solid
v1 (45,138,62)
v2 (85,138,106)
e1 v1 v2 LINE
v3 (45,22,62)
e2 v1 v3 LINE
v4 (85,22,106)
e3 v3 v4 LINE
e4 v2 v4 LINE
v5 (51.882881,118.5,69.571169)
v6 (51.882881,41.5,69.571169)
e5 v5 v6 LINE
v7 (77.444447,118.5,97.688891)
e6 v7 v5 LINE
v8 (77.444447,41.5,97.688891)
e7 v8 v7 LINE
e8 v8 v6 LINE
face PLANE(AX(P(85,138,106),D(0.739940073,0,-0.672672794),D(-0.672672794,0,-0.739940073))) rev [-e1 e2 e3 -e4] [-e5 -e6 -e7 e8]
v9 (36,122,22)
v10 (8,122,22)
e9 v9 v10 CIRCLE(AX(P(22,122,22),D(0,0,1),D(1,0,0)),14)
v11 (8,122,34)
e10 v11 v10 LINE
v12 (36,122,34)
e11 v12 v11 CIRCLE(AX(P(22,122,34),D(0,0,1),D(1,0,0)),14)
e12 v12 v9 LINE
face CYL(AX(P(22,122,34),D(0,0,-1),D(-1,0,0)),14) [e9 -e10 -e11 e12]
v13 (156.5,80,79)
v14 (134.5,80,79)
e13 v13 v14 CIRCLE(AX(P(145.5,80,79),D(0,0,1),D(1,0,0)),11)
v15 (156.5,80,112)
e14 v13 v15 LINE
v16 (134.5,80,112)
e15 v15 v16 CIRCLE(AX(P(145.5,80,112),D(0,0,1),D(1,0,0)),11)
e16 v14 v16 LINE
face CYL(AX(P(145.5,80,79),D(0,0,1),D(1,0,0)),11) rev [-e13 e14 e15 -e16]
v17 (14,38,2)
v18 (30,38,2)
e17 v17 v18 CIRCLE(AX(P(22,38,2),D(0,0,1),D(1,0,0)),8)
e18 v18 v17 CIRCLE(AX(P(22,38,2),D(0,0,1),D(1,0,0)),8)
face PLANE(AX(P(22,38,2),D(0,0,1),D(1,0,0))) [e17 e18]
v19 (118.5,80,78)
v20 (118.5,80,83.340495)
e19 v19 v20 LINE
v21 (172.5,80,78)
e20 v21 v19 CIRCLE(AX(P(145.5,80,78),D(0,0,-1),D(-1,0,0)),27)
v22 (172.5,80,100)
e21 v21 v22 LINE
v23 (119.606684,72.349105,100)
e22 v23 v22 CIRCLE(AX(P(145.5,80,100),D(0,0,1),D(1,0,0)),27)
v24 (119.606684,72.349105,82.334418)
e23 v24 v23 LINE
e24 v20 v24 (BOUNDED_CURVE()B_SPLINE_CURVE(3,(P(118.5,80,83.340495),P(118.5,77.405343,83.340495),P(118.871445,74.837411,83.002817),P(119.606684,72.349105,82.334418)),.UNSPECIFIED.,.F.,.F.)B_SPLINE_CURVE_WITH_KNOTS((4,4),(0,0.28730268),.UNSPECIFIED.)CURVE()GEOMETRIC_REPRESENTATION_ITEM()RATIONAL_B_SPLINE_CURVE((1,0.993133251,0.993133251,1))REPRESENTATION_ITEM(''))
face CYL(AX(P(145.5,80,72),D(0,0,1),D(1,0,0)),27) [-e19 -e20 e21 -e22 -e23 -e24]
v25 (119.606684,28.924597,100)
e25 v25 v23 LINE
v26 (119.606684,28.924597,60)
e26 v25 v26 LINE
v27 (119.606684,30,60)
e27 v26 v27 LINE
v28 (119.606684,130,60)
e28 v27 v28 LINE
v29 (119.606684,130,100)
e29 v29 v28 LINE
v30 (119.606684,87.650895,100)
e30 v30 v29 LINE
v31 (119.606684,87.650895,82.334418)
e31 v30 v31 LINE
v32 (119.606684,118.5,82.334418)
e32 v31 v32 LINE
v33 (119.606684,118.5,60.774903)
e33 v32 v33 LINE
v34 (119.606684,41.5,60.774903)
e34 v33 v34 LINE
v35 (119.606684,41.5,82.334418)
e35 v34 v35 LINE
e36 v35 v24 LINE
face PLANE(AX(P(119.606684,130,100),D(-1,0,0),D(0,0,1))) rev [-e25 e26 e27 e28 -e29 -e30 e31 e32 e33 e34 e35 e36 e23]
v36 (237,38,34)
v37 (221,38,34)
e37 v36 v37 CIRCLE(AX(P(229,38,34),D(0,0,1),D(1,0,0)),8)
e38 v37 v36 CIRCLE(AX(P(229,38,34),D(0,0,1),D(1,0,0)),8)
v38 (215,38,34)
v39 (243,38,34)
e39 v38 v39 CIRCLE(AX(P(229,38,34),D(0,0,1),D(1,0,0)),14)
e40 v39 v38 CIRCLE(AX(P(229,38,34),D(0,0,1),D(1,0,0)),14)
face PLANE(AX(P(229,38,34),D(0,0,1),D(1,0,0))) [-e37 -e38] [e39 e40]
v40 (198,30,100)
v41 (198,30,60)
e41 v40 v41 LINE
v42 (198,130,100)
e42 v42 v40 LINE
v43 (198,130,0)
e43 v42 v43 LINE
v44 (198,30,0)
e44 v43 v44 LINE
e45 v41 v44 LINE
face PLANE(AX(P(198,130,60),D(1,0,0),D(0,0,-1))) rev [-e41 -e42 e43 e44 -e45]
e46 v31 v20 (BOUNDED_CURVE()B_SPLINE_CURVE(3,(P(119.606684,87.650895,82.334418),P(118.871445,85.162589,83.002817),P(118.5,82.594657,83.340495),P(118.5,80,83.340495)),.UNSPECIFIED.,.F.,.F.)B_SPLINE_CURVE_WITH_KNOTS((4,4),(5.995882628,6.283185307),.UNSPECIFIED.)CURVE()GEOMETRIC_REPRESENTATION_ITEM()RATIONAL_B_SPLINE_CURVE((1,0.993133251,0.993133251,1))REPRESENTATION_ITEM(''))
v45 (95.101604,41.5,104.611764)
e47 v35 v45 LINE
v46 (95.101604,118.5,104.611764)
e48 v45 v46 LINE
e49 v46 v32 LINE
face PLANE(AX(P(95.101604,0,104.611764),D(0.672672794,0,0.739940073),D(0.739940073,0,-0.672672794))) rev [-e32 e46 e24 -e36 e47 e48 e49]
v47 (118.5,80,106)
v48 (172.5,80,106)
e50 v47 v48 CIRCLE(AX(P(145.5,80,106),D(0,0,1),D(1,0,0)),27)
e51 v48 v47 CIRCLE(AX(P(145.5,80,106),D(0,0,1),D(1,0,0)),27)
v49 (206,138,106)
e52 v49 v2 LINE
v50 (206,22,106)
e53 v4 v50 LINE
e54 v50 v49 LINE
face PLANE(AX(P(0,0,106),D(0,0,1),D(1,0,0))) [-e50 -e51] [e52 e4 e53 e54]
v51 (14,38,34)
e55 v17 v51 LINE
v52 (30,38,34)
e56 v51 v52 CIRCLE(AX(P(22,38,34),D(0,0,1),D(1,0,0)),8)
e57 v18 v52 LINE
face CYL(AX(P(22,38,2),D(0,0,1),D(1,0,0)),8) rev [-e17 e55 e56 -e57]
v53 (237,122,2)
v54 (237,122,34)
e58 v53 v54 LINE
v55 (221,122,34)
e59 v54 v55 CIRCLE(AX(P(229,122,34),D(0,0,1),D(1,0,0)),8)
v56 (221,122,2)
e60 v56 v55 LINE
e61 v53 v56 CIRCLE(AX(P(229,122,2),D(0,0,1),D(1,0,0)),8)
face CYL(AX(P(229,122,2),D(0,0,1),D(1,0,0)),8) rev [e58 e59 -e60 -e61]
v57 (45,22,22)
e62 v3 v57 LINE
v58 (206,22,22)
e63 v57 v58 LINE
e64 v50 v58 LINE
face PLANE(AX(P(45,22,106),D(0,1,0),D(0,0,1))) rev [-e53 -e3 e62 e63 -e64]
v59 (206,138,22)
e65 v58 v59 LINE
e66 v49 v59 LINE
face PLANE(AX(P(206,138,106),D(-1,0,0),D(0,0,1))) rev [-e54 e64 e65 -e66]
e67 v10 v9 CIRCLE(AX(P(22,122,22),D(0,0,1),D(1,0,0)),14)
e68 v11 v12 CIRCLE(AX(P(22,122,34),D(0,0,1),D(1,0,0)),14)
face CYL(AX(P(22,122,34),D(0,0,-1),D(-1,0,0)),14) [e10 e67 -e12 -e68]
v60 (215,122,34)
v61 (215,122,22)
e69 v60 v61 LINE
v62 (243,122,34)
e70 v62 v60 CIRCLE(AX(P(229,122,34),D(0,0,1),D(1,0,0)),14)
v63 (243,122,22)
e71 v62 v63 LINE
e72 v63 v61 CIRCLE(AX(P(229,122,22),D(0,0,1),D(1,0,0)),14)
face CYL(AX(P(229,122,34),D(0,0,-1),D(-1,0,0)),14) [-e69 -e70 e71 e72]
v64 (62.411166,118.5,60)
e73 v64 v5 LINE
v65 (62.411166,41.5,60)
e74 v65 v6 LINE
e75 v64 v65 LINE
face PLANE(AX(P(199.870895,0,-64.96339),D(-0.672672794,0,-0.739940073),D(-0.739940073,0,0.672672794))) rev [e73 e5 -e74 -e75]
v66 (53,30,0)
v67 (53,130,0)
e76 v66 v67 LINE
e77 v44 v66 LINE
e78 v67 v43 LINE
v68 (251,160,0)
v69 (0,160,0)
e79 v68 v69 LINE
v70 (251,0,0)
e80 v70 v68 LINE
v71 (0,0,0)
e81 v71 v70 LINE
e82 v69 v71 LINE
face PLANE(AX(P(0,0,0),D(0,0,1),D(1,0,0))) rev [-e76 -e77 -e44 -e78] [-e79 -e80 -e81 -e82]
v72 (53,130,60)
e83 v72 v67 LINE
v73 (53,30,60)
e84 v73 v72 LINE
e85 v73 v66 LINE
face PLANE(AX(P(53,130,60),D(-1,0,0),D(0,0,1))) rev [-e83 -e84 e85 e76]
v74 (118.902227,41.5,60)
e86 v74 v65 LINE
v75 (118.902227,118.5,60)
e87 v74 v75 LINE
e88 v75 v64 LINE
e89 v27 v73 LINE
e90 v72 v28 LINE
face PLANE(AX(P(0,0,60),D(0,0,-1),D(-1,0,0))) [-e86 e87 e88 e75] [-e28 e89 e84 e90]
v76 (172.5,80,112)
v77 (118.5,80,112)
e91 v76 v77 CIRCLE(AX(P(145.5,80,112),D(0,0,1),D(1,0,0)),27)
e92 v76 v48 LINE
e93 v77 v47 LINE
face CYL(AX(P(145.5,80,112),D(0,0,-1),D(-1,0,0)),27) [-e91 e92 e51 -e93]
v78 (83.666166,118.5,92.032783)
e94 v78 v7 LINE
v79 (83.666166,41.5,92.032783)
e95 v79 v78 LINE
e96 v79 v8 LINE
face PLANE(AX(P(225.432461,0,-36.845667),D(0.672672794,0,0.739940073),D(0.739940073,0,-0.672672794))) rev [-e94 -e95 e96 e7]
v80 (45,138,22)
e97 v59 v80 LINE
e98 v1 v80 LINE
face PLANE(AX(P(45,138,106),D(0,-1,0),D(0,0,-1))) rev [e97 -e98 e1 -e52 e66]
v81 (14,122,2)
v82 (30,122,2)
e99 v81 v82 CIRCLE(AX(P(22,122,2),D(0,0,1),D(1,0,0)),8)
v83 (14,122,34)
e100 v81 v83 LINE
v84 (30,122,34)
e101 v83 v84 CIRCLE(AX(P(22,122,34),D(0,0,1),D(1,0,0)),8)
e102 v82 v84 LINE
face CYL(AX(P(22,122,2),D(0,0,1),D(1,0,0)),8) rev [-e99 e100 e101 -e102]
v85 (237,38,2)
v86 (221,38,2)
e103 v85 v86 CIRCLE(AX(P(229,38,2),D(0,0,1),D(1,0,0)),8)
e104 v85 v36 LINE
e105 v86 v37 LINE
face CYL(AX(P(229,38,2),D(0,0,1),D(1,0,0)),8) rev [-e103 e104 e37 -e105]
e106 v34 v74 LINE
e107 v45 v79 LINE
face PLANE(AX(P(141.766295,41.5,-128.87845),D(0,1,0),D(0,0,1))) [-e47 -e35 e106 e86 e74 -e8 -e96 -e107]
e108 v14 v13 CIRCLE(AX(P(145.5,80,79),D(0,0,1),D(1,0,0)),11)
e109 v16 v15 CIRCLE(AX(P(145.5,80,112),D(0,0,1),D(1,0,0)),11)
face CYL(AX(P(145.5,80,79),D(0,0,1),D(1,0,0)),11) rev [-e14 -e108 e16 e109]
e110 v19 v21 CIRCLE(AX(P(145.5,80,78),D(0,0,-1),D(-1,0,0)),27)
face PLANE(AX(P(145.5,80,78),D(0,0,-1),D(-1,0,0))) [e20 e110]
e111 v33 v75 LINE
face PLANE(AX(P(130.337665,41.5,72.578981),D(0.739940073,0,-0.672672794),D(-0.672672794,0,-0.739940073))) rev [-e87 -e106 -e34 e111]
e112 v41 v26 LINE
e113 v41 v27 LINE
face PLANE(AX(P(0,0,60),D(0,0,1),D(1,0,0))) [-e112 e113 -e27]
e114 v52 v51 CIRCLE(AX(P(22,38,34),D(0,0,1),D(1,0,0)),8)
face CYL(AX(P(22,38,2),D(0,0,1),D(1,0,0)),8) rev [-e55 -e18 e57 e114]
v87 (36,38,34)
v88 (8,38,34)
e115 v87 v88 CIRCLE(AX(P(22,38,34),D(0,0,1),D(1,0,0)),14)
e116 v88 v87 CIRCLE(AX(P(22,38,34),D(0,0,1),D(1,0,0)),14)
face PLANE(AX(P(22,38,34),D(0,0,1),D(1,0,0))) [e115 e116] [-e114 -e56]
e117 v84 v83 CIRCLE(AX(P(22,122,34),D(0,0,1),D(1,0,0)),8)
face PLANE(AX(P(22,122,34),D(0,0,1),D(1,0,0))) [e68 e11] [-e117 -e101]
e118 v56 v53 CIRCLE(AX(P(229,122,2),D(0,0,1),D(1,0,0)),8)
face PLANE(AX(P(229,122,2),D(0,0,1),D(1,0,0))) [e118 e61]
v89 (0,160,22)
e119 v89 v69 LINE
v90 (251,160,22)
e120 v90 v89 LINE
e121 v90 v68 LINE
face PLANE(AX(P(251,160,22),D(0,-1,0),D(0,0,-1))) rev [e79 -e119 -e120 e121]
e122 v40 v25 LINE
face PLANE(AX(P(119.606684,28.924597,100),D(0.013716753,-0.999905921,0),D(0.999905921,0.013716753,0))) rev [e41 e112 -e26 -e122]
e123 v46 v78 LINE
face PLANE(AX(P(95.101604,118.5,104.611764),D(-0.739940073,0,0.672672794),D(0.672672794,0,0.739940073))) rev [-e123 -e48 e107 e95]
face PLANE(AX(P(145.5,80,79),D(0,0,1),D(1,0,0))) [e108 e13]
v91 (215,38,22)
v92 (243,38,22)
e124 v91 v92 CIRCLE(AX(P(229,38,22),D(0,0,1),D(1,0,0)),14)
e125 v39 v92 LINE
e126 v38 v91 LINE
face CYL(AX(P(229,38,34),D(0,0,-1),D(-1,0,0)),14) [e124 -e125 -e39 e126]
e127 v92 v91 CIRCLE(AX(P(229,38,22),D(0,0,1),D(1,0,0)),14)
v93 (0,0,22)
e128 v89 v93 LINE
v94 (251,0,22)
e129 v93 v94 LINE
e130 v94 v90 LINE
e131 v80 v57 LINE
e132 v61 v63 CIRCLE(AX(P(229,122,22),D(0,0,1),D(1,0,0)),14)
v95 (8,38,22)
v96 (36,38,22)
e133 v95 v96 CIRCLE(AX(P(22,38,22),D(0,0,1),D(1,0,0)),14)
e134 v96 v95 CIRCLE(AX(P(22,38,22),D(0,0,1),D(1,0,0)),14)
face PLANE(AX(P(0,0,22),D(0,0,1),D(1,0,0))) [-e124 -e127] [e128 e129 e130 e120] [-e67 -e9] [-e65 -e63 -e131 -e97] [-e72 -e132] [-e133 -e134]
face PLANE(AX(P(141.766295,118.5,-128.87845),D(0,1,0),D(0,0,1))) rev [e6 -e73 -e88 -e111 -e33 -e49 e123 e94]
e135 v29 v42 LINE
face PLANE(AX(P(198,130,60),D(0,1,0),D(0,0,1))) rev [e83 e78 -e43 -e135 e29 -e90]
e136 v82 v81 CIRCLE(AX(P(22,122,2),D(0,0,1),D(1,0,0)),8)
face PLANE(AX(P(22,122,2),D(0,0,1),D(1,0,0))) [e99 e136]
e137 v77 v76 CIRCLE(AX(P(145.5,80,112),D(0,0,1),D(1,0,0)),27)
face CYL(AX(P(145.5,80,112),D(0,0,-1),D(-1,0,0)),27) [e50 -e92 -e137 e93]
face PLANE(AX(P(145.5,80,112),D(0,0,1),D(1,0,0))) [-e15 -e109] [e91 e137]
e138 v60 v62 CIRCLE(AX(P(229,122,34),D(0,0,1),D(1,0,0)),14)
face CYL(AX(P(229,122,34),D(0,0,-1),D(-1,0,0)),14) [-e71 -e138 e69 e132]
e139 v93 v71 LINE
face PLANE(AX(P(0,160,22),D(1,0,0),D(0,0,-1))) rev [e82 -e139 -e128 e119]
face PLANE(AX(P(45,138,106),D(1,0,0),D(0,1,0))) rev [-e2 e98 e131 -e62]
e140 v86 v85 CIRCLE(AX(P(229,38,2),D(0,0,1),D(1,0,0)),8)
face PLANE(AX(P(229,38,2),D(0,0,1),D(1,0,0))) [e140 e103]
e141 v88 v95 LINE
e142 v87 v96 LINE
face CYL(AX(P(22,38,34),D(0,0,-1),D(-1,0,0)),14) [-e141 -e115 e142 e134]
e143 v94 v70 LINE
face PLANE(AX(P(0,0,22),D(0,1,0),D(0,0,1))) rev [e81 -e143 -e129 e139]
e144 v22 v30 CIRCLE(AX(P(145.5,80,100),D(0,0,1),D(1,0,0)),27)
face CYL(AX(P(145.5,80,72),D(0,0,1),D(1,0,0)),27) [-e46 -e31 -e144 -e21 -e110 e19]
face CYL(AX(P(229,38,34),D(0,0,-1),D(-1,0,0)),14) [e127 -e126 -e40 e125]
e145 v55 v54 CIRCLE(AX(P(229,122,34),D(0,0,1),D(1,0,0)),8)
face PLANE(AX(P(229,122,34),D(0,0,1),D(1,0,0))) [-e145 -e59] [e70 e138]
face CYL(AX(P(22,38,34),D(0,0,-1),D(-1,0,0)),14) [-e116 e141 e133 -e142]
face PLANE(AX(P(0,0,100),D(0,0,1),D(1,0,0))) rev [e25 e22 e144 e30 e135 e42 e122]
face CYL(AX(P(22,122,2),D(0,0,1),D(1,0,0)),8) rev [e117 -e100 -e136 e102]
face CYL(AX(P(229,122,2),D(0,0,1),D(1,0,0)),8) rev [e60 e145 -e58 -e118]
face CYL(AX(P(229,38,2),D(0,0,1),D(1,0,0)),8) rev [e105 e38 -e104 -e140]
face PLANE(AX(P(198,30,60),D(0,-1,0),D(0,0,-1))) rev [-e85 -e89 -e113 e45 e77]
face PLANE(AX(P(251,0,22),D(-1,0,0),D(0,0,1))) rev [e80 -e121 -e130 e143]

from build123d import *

# Parameters (mm, degrees)
BASE_PLATE_SKETCH_W           = 251
BASE_PLATE_SKETCH_H           = 160
BASE_PLATE_DEPTH              = 22
HOUSING_BLOCK_SKETCH_W        = 161
HOUSING_BLOCK_SKETCH_H        = 116
HOUSING_BLOCK_DEPTH           = 84
HOUSING_PROFILE_CUT_DEPTH     = 116
HOUSING_TRIM_CUT_SKETCH_W     = 38
HOUSING_TRIM_CUT_SKETCH_H     = 77
HOUSING_TRIM_CUT_DEPTH        = 200
MOUNTING_BOSSES_SKETCH_R      = 14
MOUNTING_BOSSES_DEPTH         = 12
MOUNTING_HOLES_SET_1_SKETCH_R = 8
MOUNTING_HOLES_SET_1_DEPTH    = 20
MOUNTING_HOLES_SET_2_SKETCH_R = 8
MOUNTING_HOLES_SET_2_DEPTH    = 20
HOUSING_POCKET_SKETCH_W       = 145
HOUSING_POCKET_SKETCH_H       = 100
HOUSING_POCKET_DEPTH          = 60
INNER_POCKET_DEPTH            = 40
POCKET_STEP_CUT_SKETCH_W      = 47.620155069
POCKET_STEP_CUT_SKETCH_H      = 77
POCKET_STEP_CUT_DEPTH         = 17
BEARING_HUB_54_SKETCH_R       = 27
BEARING_HUB_54_DEPTH          = 34
FRONT_START                   = 6
FRONT_BOSS_54_SKETCH_R        = 27
FRONT_BOSS_54_DEPTH           = 6
HUB_START                     = -6
HUB_RECESS_54_SKETCH_R        = 27
HUB_RECESS_54_DEPTH           = 6
SHAFT_BORE_22_SKETCH_R        = 11
SHAFT_BORE_22_DEPTH           = 33


with BuildPart() as part:
    # Base Plate Sketch → Base Plate (new body)
    with BuildSketch(Plane.XY):
        with Locations((125.5, 80)):
            Rectangle(BASE_PLATE_SKETCH_W, BASE_PLATE_SKETCH_H)
    extrude(amount=BASE_PLATE_DEPTH)

    # Housing Block Sketch → Housing Block (add)
    with BuildSketch(Plane.XY.offset(22)):
        with Locations((125.5, 80)):
            Rectangle(HOUSING_BLOCK_SKETCH_W, HOUSING_BLOCK_SKETCH_H)
    extrude(amount=HOUSING_BLOCK_DEPTH)

    # Housing Profile Cut Sketch → Housing Profile Cut (cut)
    with BuildSketch(Plane.XZ.offset(-22)):
        Polygon((85, 106), (45, 62), (45, 106), align=None)
    extrude(amount=-HOUSING_PROFILE_CUT_DEPTH, mode=Mode.SUBTRACT)

    # Housing Trim Cut Sketch → Housing Trim Cut (cut)
    with BuildSketch(Plane(origin=(-6.221719457, 0, 5.656108597), x_dir=(0.6726727939963125, 0, 0.7399400733959438), z_dir=(-0.7399400733959438, 0, 0.6726727939963125))):
        with Locations((105.378697775, 80)):
            Rectangle(HOUSING_TRIM_CUT_SKETCH_W, HOUSING_TRIM_CUT_SKETCH_H)
    extrude(amount=-HOUSING_TRIM_CUT_DEPTH, mode=Mode.SUBTRACT)

    # Mounting Bosses Sketch → Mounting Bosses (add)
    with BuildSketch(Plane.XY.offset(22)):
        with Locations((229, 122)):
            Circle(MOUNTING_BOSSES_SKETCH_R)
        with Locations((229, 38)):
            Circle(MOUNTING_BOSSES_SKETCH_R)
        with Locations((22, 38)):
            Circle(MOUNTING_BOSSES_SKETCH_R)
        with Locations((22, 122)):
            Circle(MOUNTING_BOSSES_SKETCH_R)
    extrude(amount=MOUNTING_BOSSES_DEPTH)

    # Mounting Holes Set 1 Sketch → Mounting Holes Set 1 (cut)
    with BuildSketch(Plane.XY.offset(22)):
        with Locations((22, 122)):
            Circle(MOUNTING_HOLES_SET_1_SKETCH_R)
        with Locations((22, 38)):
            Circle(MOUNTING_HOLES_SET_1_SKETCH_R)
        with Locations((229, 38)):
            Circle(MOUNTING_HOLES_SET_1_SKETCH_R)
        with Locations((229, 122)):
            Circle(MOUNTING_HOLES_SET_1_SKETCH_R)
    extrude(amount=-MOUNTING_HOLES_SET_1_DEPTH, mode=Mode.SUBTRACT)

    # Mounting Holes Set 2 Sketch → Mounting Holes Set 2 (cut)
    with BuildSketch(Plane.XY.offset(34)):
        with Locations((229, 122)):
            Circle(MOUNTING_HOLES_SET_2_SKETCH_R)
        with Locations((229, 38)):
            Circle(MOUNTING_HOLES_SET_2_SKETCH_R)
        with Locations((22, 38)):
            Circle(MOUNTING_HOLES_SET_2_SKETCH_R)
        with Locations((22, 122)):
            Circle(MOUNTING_HOLES_SET_2_SKETCH_R)
    extrude(amount=-MOUNTING_HOLES_SET_2_DEPTH, mode=Mode.SUBTRACT)

    # Housing Pocket Sketch → Housing Pocket (cut)
    with BuildSketch(Plane(origin=(0, 0, 0), x_dir=(-1, 0, 0), z_dir=(0, 0, -1))):
        with Locations((-125.5, 80)):
            Rectangle(HOUSING_POCKET_SKETCH_W, HOUSING_POCKET_SKETCH_H)
    extrude(amount=-HOUSING_POCKET_DEPTH, mode=Mode.SUBTRACT)

    # Inner Pocket Sketch → Inner Pocket (cut)
    with BuildSketch(Plane(origin=(0, 0, 60), x_dir=(-1, 0, 0), z_dir=(0, 0, -1))):
        Polygon((-198, 130), (-119.606684276, 130), (-119.606684276, 28.92459706), (-198, 30), align=None)
    extrude(amount=-INNER_POCKET_DEPTH, mode=Mode.SUBTRACT)

    # Pocket Step Cut Sketch → Pocket Step Cut (cut)
    with BuildSketch(Plane(origin=(83.666166146, 0, 92.032782761), x_dir=(-0.7399400733959437, 0, 0.6726727939963125), z_dir=(-0.6726727939963125, 0, -0.7399400733959437))):
        with Locations((-23.810077535, 80)):
            Rectangle(POCKET_STEP_CUT_SKETCH_W, POCKET_STEP_CUT_SKETCH_H)
    extrude(amount=-POCKET_STEP_CUT_DEPTH, mode=Mode.SUBTRACT)

    # Bearing Hub Ø54 Sketch → Bearing Hub Ø54 (add)
    with BuildSketch(Plane.XY.offset(106)):
        with Locations((145.5, 80)):
            Circle(BEARING_HUB_54_SKETCH_R)
    extrude(amount=-BEARING_HUB_54_DEPTH)

    # Front Boss Ø54 Sketch → Front Boss Ø54 (add)
    with BuildSketch(Plane.XY.offset(106).offset(FRONT_START)):
        with Locations((145.5, 80)):
            Circle(FRONT_BOSS_54_SKETCH_R)
    extrude(amount=-FRONT_BOSS_54_DEPTH)

    # Hub Recess Ø54 Sketch → Hub Recess Ø54 (cut)
    with BuildSketch(Plane(origin=(0, 0, 72), x_dir=(-1, 0, 0), z_dir=(0, 0, -1)).offset(HUB_START)):
        with Locations(Location((-145.5, 80, 0), (0, 0, 16.461230985))):
            Circle(HUB_RECESS_54_SKETCH_R)
    extrude(amount=HUB_RECESS_54_DEPTH, mode=Mode.SUBTRACT)

    # Shaft Bore Ø22 Sketch → Shaft Bore Ø22 (cut)
    with BuildSketch(Plane.XY.offset(112)):
        with Locations((145.5, 80)):
            Circle(SHAFT_BORE_22_SKETCH_R)
    extrude(amount=-SHAFT_BORE_22_DEPTH, mode=Mode.SUBTRACT)


solid = part.part
